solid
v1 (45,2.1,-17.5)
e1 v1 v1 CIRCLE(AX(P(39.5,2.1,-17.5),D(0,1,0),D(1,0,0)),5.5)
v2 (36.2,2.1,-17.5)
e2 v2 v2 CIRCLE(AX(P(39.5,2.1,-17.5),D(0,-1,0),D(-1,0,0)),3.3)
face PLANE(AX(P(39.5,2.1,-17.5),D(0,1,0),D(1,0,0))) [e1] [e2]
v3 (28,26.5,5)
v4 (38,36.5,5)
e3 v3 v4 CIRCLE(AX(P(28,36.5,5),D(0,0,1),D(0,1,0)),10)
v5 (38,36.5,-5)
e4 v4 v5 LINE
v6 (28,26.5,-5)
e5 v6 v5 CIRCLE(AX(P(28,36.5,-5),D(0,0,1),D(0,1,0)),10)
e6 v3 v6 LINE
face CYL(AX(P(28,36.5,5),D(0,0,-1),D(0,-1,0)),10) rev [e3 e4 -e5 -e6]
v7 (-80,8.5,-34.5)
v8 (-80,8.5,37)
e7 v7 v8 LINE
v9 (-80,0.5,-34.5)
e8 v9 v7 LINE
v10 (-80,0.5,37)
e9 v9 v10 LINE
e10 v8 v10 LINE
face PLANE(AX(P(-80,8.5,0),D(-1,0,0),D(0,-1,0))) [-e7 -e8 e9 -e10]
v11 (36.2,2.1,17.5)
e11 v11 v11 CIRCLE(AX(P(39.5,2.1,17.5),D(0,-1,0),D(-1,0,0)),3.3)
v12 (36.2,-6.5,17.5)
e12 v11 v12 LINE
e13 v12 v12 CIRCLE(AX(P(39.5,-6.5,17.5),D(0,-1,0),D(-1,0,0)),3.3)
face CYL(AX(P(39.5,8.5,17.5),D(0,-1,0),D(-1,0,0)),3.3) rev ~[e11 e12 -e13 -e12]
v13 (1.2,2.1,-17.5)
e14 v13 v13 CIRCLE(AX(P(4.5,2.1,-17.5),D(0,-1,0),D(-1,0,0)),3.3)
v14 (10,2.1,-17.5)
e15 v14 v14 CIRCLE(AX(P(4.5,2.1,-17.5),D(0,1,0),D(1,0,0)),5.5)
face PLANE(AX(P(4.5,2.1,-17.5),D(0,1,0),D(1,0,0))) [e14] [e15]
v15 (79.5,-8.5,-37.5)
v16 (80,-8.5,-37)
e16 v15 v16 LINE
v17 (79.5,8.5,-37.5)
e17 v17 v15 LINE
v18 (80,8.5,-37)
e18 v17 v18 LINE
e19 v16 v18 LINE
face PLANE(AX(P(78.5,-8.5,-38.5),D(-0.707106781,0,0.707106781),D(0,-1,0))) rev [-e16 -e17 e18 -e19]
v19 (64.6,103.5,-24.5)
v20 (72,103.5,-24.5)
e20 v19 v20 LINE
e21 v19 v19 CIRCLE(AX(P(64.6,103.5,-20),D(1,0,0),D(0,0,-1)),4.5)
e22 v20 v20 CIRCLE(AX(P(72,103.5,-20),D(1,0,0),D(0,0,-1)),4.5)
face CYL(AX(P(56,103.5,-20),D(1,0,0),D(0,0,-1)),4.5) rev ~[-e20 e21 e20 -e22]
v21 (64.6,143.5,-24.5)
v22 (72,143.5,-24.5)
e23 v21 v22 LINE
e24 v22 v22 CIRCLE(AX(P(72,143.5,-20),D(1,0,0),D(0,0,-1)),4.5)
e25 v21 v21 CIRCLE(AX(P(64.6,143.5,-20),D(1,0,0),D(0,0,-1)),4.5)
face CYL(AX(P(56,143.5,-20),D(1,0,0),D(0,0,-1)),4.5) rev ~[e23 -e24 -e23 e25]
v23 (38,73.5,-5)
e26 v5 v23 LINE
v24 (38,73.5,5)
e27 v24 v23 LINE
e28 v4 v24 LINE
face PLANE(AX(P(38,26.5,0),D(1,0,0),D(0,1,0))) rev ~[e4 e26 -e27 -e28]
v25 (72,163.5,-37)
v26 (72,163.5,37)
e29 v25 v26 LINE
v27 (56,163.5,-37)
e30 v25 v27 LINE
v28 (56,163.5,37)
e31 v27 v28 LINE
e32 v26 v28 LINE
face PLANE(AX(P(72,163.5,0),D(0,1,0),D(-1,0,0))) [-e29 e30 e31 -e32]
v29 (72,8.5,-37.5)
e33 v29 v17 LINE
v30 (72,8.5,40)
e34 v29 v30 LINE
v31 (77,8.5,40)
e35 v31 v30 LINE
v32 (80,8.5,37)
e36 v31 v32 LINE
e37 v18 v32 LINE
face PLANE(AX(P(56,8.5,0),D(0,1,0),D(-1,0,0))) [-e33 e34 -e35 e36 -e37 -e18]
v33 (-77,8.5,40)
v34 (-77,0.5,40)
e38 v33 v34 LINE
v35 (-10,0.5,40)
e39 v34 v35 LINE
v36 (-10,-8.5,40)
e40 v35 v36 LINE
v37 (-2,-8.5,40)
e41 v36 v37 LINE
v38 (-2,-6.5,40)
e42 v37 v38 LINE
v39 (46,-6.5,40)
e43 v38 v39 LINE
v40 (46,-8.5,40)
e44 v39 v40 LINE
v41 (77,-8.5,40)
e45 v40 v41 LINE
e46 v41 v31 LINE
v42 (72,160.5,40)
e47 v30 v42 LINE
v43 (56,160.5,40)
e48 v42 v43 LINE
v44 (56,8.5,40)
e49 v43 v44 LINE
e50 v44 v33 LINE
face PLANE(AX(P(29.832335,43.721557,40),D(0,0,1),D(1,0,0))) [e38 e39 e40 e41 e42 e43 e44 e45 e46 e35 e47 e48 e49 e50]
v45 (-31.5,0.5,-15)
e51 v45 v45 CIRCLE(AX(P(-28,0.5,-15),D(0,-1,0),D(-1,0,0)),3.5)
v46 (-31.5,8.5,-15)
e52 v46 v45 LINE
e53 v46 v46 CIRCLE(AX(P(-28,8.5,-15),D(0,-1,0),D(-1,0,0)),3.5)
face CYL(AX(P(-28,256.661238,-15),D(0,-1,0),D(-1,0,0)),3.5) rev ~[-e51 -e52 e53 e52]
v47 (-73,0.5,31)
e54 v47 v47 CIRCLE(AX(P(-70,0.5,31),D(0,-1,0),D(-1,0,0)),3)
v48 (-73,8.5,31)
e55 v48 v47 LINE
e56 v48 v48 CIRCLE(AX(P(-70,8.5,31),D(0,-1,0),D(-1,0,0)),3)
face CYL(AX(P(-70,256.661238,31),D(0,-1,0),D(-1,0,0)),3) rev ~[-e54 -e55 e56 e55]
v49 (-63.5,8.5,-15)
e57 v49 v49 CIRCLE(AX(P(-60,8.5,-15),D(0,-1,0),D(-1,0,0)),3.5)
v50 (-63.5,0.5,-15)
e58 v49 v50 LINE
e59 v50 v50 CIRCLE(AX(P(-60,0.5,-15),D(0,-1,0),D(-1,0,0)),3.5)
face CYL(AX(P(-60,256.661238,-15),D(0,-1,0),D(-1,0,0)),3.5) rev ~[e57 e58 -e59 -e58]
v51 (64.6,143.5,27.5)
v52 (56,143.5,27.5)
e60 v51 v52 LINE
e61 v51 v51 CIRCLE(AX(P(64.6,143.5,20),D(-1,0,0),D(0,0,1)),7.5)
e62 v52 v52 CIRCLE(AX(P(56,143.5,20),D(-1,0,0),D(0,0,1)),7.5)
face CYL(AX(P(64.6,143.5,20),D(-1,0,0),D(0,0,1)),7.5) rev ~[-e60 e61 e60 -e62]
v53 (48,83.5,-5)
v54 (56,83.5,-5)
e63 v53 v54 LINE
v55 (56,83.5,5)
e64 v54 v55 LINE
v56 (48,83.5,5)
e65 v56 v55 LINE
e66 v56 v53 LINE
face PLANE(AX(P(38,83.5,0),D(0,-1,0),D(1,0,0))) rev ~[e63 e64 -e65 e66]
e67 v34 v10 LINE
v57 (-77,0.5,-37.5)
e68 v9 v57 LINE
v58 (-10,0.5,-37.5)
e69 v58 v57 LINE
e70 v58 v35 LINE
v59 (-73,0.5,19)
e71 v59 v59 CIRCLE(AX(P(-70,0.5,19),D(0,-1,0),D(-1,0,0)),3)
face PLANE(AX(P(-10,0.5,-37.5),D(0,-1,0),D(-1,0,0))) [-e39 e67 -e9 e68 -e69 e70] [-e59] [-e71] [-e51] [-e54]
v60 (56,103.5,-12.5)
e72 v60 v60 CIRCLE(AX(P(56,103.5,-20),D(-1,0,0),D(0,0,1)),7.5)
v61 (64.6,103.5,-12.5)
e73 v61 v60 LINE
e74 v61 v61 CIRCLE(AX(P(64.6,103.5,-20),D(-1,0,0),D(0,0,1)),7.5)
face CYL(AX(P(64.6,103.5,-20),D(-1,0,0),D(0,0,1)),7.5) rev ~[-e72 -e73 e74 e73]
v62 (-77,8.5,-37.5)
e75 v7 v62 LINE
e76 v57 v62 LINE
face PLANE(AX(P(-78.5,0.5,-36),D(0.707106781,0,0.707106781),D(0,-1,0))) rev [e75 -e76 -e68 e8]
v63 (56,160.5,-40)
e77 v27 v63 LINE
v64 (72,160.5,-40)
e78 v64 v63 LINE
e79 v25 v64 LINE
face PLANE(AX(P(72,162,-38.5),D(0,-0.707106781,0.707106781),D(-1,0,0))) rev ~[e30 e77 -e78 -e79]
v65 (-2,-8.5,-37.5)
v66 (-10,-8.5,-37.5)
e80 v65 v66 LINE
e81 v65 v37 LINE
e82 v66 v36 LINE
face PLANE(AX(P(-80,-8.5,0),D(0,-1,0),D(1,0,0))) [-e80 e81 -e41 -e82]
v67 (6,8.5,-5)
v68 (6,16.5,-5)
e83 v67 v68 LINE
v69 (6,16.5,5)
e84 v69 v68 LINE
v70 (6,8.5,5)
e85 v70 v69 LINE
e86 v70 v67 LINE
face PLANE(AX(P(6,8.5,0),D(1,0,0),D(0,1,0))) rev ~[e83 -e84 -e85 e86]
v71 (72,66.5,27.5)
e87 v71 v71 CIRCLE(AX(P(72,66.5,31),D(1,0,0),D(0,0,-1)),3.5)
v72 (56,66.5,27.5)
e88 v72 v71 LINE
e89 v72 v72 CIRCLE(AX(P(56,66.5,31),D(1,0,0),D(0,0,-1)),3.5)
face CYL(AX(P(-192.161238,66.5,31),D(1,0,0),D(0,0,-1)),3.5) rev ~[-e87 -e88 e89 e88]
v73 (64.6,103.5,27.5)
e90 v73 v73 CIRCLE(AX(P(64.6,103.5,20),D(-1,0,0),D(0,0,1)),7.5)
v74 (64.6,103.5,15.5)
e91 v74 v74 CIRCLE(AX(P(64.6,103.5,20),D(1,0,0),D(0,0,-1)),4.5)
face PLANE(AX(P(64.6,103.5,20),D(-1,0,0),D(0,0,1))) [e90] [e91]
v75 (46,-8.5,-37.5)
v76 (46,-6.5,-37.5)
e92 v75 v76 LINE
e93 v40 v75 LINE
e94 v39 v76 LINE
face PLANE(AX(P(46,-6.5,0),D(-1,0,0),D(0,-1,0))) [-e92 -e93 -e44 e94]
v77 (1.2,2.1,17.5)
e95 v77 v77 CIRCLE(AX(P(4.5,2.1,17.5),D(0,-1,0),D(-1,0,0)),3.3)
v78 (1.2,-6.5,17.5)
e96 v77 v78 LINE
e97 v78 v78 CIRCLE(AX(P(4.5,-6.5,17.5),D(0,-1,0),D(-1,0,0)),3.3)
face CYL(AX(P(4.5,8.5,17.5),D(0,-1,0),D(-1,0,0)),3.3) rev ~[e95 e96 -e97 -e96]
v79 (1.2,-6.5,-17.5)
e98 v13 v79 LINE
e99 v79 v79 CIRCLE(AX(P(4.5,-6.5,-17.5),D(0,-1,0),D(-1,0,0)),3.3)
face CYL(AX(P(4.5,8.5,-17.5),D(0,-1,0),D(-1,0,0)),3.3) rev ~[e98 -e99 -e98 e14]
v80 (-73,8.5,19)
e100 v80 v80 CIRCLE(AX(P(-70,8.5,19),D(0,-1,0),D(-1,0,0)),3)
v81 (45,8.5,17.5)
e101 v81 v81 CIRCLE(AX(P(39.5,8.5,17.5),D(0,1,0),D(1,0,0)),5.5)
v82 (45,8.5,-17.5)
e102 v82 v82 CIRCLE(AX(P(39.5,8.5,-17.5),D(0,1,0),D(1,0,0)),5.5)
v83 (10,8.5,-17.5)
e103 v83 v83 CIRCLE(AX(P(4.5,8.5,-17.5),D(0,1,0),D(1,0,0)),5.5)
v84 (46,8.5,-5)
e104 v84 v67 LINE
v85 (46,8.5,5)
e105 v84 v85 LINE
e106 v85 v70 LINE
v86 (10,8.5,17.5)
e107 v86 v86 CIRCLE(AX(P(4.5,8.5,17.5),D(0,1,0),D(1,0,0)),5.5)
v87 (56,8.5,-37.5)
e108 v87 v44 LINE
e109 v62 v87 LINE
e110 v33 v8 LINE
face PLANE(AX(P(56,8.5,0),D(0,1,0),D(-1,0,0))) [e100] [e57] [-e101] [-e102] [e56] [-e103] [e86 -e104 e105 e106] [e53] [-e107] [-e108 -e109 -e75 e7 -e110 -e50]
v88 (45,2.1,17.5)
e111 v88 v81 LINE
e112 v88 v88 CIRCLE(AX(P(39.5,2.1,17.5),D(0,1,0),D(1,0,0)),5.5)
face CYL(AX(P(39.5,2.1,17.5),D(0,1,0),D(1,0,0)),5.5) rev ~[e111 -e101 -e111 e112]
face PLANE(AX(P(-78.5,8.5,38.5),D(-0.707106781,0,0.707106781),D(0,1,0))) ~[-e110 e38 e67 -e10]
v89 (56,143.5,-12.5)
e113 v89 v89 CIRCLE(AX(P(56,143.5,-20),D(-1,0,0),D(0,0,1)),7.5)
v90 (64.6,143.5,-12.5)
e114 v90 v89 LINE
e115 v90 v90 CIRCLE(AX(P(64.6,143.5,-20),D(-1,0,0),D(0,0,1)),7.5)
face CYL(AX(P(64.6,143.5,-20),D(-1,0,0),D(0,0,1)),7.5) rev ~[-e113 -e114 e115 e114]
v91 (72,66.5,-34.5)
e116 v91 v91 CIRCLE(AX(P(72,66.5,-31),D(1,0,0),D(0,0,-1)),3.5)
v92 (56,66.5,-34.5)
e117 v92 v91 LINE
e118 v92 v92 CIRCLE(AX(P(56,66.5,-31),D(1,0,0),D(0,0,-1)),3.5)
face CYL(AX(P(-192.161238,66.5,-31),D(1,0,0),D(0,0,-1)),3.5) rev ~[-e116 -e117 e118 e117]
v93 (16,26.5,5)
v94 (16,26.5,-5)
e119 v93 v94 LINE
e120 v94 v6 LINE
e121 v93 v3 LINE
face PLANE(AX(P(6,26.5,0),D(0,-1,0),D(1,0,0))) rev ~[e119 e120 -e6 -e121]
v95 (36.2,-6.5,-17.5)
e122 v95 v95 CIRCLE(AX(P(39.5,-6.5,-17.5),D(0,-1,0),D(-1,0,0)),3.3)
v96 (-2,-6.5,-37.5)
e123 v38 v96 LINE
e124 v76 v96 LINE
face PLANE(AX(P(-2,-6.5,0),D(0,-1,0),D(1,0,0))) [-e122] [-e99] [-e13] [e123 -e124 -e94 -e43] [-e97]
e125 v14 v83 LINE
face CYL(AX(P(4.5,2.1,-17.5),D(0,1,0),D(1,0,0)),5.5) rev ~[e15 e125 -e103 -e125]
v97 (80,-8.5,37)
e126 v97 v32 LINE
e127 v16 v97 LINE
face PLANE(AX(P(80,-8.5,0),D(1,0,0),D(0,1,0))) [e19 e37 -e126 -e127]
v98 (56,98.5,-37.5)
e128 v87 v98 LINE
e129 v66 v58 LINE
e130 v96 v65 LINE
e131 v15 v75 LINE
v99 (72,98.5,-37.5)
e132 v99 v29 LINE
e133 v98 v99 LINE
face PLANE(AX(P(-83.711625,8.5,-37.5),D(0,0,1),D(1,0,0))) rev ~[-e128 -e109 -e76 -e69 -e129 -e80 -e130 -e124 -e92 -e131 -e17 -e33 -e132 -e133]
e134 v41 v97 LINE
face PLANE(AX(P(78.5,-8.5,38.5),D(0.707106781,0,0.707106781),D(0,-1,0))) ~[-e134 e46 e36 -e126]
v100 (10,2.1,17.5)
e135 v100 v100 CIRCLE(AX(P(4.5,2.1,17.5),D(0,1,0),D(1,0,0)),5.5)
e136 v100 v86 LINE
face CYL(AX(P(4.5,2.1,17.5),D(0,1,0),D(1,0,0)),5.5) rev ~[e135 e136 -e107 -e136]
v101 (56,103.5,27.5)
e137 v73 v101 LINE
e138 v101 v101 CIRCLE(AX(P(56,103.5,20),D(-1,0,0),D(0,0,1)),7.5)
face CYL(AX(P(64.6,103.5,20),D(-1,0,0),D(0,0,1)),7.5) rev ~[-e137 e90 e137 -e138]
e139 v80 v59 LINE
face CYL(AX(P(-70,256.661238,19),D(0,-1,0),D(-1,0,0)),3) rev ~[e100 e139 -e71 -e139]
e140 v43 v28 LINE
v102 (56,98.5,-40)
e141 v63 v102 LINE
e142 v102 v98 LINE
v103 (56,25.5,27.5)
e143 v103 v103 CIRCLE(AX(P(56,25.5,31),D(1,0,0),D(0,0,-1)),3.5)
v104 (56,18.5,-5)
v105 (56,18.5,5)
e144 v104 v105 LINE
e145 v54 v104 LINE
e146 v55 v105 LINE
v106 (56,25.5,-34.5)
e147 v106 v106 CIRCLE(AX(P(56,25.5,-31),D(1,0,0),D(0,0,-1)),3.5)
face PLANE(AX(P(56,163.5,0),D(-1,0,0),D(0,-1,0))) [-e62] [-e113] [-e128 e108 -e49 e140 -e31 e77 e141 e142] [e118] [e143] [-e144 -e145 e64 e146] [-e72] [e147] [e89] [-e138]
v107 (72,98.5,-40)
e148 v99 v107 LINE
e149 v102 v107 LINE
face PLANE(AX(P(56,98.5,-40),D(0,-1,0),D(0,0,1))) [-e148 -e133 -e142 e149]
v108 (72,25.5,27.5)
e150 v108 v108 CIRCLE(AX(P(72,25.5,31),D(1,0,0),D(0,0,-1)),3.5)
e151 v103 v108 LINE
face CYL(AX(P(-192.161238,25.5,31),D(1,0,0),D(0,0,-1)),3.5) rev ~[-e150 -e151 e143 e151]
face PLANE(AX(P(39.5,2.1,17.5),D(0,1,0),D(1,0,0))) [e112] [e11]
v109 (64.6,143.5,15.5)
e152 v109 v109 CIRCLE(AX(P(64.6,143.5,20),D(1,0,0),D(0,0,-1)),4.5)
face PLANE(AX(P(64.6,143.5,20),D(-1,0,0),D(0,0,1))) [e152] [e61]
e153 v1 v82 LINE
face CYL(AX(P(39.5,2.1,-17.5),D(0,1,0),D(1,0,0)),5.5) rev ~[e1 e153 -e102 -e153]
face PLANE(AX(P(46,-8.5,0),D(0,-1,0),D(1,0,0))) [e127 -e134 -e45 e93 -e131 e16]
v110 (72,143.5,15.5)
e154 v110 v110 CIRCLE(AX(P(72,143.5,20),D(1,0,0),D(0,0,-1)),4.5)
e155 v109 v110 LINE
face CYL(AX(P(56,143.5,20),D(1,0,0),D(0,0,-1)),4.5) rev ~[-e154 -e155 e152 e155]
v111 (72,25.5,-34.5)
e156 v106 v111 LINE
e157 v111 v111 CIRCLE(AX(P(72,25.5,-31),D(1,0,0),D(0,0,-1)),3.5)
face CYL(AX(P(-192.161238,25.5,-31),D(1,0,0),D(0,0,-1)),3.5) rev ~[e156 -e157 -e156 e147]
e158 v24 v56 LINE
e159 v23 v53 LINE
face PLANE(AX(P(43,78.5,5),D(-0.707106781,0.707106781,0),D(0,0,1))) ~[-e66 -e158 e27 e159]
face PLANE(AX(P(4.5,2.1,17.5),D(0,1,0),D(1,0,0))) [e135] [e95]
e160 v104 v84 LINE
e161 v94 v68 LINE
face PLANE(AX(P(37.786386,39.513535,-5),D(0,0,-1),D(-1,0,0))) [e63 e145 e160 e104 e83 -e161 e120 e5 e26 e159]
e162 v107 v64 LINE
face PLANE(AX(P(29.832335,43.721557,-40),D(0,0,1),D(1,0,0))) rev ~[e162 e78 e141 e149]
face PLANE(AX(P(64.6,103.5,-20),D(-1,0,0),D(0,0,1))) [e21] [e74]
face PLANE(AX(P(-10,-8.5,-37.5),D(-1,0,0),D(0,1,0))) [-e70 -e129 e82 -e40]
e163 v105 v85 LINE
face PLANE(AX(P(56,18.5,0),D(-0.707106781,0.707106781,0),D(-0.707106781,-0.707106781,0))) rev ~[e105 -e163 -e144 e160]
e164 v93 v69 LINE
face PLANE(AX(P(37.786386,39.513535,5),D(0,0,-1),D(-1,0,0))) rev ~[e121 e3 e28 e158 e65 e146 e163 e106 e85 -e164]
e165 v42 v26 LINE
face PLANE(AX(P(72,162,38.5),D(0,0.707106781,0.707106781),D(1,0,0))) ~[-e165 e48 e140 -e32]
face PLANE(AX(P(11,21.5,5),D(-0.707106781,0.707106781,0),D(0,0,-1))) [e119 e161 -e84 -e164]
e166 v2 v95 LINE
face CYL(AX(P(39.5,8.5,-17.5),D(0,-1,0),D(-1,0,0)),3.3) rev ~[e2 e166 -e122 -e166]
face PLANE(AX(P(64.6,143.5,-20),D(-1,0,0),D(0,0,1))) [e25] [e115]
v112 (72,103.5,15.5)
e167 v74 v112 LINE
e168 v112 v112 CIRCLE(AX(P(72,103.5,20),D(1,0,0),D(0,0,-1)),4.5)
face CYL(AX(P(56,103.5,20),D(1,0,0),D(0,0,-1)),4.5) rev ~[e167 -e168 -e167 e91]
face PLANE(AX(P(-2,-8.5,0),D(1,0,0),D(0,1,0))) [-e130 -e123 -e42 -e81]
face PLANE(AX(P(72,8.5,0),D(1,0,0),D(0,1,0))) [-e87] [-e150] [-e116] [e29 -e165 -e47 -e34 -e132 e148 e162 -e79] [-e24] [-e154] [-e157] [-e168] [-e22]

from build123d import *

# Parameters (mm, degrees)
EXTRUDE_2_DEPTH              = 40
SKETCH_4_W                   = 2.5
SKETCH_4_H                   = 90
CUT_EXTRUDE_2_DEPTH          = 80
EXTRUDE_3_DEPTH              = 5
FILLET_1_R                   = 10
CHAMFER_1_SIZE               = 10
HOLE_WIZARD_M6_1_D           = 6.6
HOLE_WIZARD_M6_1_CBORE_D     = 11
HOLE_WIZARD_M6_1_CBORE_DEPTH = 6.4
CHAMFER_2_SIZE               = 3
HOLE_WIZARD_7_0_7_1_D        = 7
HOLE_WIZARD_M8_2_D           = 9
HOLE_WIZARD_M8_2_CBORE_D     = 15
HOLE_WIZARD_M8_2_CBORE_DEPTH = 8.6
SKETCH_16_W                  = 163.711624667
SKETCH_16_H                  = 2.5
CUT_EXTRUDE_3_DEPTH          = 179.955301682
SKETCH_17_W                  = 70
SKETCH_17_H                  = 9
CUT_EXTRUDE_4_DEPTH          = 198.834526815
CHAMFER_4_SIZE               = 3
HOLE_WIZARD_7_0_7_2_D        = 7
HOLE_WIZARD_6_0_6_1_D        = 6


with BuildPart() as part:
    # 草图2 → 凸台-拉伸2 (new, symmetric)
    with BuildSketch(Plane.XY):
        Polygon((46, -8.5), (80, -8.5), (80, 8.5), (72, 8.5), (72, 163.5), (56, 163.5), (56, 8.5), (-80, 8.5), (-80, -8.5), (-2, -8.5), (-2, -6.5), (46, -6.5), align=None)
    extrude(amount=EXTRUDE_2_DEPTH, both=True)

    # 草图4 → 切除-拉伸2 (cut)
    with BuildSketch(Plane.ZY.offset(-56)):
        with Locations((-38.75, 53.5)):
            Rectangle(SKETCH_4_W, SKETCH_4_H)
    extrude(amount=-CUT_EXTRUDE_2_DEPTH, mode=Mode.SUBTRACT)

    # 草图5 → 凸台-拉伸3 (add, symmetric)
    with BuildSketch(Plane.XY):
        Polygon((46, 8.5), (6, 8.5), (6, 26.5), (38, 26.5), (38, 83.5), (56, 83.5), (56, 18.5), align=None)
    extrude(amount=EXTRUDE_3_DEPTH, both=True)

    # 圆角1
    fillet_1_edges = [part.edges().sort_by_distance(p)[0] for p in [
        (38, 26.5, 0),
    ]]
    fillet(fillet_1_edges, radius=FILLET_1_R)

    # 倒角1
    chamfer_1_edges = [part.edges().sort_by_distance(p)[0] for p in [
        (6, 26.5, 0),
        (38, 83.5, 0),
    ]]
    chamfer(chamfer_1_edges, length=CHAMFER_1_SIZE)

    # M6 六角凹头螺钉的柱形沉头孔1 (through all)
    with Locations(Plane(origin=(0, 8.5, 0), x_dir=(1, 0, 0), z_dir=(0, 1, 0))):
        with Locations((4.5, 17.5), (39.5, 17.5), (39.5, -17.5), (4.5, -17.5)):
            CounterBoreHole(HOLE_WIZARD_M6_1_D / 2, HOLE_WIZARD_M6_1_CBORE_D / 2, HOLE_WIZARD_M6_1_CBORE_DEPTH)

    # 倒角2
    chamfer_2_edges = [part.edges().sort_by_distance(p)[0] for p in [
        (64, 163.5, 40),
        (64, 163.5, -40),
        (80, 0, -40),
        (-80, 0, 40),
        (80, 0, 40),
    ]]
    chamfer(chamfer_2_edges, length=CHAMFER_2_SIZE)

    # Ø7.0 (7) 直径孔1 (through all)
    with Locations(Plane.ZY.offset(-56)):
        with Locations((-31, 25.5), (-31, 66.5), (31, 66.5), (31, 25.5)):
            Hole(HOLE_WIZARD_7_0_7_1_D / 2)

    # M8 六角凹头螺钉的柱形沉头孔2 (through all)
    with Locations(Plane.ZY.offset(-56)):
        with Locations((-20, 143.5), (-20, 103.5), (20, 103.5), (20, 143.5)):
            CounterBoreHole(HOLE_WIZARD_M8_2_D / 2, HOLE_WIZARD_M8_2_CBORE_D / 2, HOLE_WIZARD_M8_2_CBORE_DEPTH)

    # 草图16 → 切除-拉伸3 (cut, through all)
    with BuildSketch(Plane(origin=(0, 8.5, 0), x_dir=(1, 0, 0), z_dir=(0, 1, 0))):
        with Locations((-1.855812334, 38.75)):
            Rectangle(SKETCH_16_W, SKETCH_16_H)
    extrude(amount=-CUT_EXTRUDE_3_DEPTH, mode=Mode.SUBTRACT)

    # 草图17 → 切除-拉伸4 (cut, through all)
    with BuildSketch(Plane(origin=(0, 0, -37.5), x_dir=(-1, 0, 0), z_dir=(0, 0, -1))):
        with Locations((45, -4)):
            Rectangle(SKETCH_17_W, SKETCH_17_H)
    extrude(amount=-CUT_EXTRUDE_4_DEPTH, mode=Mode.SUBTRACT)

    # 倒角4
    chamfer_4_edges = [part.edges().sort_by_distance(p)[0] for p in [
        (-80, 4.5, -37.5),
    ]]
    chamfer(chamfer_4_edges, length=CHAMFER_4_SIZE)

    # Ø7.0 (7) 直径孔2 (through all)
    with Locations(Plane(origin=(0, 8.5, 0), x_dir=(1, 0, 0), z_dir=(0, 1, 0))):
        with Locations((-28, 15), (-60, 15)):
            Hole(HOLE_WIZARD_7_0_7_2_D / 2)

    # Ø6.0 (6) 直径孔1 (through all)
    with Locations(Plane(origin=(0, 8.5, 0), x_dir=(1, 0, 0), z_dir=(0, 1, 0))):
        with Locations((-70, -31), (-70, -19)):
            Hole(HOLE_WIZARD_6_0_6_1_D / 2)


solid = part.part
